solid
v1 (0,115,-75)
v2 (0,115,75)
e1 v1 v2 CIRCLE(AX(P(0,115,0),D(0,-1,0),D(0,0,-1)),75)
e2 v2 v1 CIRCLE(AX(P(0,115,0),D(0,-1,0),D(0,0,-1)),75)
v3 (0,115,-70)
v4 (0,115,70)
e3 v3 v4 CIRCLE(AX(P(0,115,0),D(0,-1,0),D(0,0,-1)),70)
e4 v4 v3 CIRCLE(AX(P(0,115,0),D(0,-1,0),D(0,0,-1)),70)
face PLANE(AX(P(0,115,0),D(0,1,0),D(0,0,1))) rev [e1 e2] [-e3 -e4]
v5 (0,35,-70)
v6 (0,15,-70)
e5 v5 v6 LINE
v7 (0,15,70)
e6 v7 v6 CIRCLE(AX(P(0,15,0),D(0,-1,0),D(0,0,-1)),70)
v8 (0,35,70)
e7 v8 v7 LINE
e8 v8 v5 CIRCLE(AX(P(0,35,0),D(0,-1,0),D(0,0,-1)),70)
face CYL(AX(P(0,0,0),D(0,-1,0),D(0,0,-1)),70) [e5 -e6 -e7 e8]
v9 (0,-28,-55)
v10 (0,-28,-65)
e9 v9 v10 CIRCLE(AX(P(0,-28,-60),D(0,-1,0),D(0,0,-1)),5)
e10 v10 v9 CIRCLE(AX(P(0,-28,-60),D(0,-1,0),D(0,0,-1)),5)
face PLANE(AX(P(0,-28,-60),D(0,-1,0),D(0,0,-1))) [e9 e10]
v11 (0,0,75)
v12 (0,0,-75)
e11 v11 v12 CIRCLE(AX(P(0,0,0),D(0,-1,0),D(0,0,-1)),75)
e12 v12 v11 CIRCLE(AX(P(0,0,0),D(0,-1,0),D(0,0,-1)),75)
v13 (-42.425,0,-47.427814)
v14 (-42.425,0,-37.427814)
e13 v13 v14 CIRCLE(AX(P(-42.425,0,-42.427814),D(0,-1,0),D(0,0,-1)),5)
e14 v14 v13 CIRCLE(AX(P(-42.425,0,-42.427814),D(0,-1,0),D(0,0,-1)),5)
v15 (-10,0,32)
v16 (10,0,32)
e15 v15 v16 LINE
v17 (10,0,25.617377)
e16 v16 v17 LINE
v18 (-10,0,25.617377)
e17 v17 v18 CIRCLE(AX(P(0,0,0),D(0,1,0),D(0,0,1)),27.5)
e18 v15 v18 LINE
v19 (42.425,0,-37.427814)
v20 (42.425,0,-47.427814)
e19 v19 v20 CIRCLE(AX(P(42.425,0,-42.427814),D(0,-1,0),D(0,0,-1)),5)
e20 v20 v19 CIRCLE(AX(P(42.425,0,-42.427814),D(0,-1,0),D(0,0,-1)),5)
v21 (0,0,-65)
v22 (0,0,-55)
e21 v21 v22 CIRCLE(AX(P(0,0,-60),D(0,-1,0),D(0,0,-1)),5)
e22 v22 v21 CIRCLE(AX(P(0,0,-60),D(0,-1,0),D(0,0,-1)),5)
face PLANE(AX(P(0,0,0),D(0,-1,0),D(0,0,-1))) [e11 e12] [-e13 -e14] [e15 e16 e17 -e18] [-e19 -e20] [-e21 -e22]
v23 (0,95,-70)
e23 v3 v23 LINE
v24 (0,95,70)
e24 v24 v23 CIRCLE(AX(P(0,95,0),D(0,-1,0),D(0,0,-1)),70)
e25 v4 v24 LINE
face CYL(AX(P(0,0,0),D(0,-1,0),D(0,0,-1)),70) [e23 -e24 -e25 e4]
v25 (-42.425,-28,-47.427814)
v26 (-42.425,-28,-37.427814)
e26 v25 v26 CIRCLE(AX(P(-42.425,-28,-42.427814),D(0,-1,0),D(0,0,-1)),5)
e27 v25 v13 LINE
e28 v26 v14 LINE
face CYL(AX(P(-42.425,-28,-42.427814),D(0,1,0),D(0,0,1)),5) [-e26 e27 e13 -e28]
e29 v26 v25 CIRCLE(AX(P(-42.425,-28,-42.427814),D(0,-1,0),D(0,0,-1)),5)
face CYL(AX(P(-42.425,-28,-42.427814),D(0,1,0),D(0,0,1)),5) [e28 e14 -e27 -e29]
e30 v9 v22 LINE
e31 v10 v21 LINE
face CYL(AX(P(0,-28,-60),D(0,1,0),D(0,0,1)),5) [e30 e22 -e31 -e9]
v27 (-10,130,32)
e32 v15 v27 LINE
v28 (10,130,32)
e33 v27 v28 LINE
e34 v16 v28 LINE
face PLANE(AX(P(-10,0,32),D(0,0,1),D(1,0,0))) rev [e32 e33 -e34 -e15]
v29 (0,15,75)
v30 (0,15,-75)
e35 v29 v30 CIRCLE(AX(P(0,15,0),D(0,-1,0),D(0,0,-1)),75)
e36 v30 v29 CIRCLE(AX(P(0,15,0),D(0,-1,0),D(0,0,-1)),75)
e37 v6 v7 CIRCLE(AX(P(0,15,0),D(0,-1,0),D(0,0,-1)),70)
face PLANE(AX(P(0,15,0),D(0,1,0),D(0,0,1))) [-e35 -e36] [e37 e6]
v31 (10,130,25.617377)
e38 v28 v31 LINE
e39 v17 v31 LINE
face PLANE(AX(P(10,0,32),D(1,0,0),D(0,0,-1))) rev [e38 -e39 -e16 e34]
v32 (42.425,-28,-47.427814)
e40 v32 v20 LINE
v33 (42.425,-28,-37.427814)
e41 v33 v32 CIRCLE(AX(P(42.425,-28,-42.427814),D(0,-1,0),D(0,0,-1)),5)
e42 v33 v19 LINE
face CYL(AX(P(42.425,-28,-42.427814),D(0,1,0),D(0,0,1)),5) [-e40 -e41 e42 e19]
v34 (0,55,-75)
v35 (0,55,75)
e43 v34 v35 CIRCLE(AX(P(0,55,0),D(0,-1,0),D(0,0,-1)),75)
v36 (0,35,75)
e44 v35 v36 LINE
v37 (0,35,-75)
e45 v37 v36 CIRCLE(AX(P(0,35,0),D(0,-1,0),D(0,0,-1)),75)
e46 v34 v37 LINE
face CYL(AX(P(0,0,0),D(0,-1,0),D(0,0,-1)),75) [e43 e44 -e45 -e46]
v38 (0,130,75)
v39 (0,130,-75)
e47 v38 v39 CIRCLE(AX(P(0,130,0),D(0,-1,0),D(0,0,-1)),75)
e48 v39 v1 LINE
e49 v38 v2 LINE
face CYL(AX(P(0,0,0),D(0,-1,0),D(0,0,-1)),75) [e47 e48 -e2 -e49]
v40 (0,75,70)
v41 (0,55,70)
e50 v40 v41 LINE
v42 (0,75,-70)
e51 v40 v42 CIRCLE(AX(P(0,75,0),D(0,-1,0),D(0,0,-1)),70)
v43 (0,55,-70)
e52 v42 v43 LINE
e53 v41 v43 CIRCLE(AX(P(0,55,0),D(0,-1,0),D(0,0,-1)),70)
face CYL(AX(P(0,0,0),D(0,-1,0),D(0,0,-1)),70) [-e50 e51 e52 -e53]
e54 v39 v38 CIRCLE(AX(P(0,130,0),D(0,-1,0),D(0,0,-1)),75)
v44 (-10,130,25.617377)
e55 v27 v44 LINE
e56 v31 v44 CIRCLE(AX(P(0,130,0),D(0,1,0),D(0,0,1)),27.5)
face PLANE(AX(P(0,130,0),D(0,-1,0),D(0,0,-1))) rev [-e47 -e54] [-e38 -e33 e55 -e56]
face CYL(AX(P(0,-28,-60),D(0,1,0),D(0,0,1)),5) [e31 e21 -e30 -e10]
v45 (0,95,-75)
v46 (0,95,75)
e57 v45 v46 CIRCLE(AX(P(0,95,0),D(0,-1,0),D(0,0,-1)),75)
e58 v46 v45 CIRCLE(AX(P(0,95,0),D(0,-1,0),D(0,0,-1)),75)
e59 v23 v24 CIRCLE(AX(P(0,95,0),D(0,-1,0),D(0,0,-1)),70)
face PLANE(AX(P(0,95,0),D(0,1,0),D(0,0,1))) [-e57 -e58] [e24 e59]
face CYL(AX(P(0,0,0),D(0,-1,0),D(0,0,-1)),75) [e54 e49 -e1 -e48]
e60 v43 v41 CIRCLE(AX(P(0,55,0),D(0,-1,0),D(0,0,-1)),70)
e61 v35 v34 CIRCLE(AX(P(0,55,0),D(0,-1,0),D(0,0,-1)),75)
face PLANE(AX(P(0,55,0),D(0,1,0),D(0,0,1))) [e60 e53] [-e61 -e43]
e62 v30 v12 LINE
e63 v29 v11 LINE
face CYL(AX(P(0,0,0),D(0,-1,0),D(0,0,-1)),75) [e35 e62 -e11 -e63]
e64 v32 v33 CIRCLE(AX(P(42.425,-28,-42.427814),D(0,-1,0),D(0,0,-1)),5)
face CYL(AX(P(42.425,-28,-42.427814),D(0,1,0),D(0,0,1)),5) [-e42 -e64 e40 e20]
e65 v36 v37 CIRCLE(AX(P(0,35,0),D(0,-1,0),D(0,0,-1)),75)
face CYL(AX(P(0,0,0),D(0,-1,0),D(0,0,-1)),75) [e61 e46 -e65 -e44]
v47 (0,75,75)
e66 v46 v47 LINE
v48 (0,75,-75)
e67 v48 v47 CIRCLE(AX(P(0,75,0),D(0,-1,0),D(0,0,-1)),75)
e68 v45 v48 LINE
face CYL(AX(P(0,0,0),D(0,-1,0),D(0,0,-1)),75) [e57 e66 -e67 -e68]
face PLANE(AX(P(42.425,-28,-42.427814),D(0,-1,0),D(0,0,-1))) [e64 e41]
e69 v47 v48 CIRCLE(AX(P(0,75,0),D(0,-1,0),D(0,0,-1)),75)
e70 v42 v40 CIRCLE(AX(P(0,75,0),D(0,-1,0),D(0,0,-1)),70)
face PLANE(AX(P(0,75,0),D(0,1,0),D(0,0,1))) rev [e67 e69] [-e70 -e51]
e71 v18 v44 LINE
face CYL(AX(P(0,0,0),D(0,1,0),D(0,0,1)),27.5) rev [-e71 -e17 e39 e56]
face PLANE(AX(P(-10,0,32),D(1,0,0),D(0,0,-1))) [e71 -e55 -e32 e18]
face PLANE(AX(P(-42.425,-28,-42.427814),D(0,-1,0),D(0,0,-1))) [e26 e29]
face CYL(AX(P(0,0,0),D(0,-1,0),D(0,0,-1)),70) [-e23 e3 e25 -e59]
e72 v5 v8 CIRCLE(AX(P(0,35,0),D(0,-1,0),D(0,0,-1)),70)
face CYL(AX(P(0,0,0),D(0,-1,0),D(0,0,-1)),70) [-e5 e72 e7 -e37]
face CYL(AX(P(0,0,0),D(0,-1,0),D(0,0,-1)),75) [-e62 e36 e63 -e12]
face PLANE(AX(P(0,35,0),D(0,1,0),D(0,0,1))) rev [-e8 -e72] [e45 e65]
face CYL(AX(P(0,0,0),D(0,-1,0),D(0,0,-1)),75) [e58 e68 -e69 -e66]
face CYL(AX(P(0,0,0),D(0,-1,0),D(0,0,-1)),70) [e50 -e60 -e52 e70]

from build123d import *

# Parameters (mm, degrees)
SKETCH3_R           = 27.5
SKETCH3_W           = 20
SKETCH3_H           = 9
CUT_EXTRUDE1_DEPTH  = 130
SKETCH4_R           = 5
BOSS_EXTRUDE3_DEPTH = 28


with BuildPart() as part:
    # Sketch 1 → Revolve1 (revolve)
    with BuildSketch(Plane.XY, mode=Mode.PRIVATE) as revolve1_sk:
        Polygon((70, 75), (75, 75), (75, 95), (70, 95), (70, 115), (75, 115), (75, 130), (0, 130), (0, 0), (75, 0), (75, 15), (70, 15), (70, 35), (75, 35), (75, 55), (70, 55), align=None)
    revolve(revolve1_sk.sketch.rotate(Axis((0, 0, 0), (0, 1, 0)), 90), axis=Axis((0, 0, 0), (0, 1, 0)))

    # Sketch3 → Cut-Extrude1 (cut)
    with BuildSketch(Plane(origin=(0, 130, 0), x_dir=(1, 0, 0), z_dir=(0, 1, 0))):
        Circle(SKETCH3_R)
        with Locations((0, -27.5)):
            Rectangle(SKETCH3_W, SKETCH3_H)
    extrude(amount=-CUT_EXTRUDE1_DEPTH, mode=Mode.SUBTRACT)

    # Sketch4 → Boss-Extrude3 (add)
    with BuildSketch(Plane.XZ):
        with Locations(Location((0, -60, 0), (0, 0, 270))):
            Circle(SKETCH4_R)
        with Locations(Location((42.425, -42.427813696, 0), (0, 0, 270))):
            Circle(SKETCH4_R)
        with Locations(Location((-42.425, -42.427813696, 0), (0, 0, 270))):
            Circle(SKETCH4_R)
    extrude(amount=BOSS_EXTRUDE3_DEPTH)


solid = part.part
